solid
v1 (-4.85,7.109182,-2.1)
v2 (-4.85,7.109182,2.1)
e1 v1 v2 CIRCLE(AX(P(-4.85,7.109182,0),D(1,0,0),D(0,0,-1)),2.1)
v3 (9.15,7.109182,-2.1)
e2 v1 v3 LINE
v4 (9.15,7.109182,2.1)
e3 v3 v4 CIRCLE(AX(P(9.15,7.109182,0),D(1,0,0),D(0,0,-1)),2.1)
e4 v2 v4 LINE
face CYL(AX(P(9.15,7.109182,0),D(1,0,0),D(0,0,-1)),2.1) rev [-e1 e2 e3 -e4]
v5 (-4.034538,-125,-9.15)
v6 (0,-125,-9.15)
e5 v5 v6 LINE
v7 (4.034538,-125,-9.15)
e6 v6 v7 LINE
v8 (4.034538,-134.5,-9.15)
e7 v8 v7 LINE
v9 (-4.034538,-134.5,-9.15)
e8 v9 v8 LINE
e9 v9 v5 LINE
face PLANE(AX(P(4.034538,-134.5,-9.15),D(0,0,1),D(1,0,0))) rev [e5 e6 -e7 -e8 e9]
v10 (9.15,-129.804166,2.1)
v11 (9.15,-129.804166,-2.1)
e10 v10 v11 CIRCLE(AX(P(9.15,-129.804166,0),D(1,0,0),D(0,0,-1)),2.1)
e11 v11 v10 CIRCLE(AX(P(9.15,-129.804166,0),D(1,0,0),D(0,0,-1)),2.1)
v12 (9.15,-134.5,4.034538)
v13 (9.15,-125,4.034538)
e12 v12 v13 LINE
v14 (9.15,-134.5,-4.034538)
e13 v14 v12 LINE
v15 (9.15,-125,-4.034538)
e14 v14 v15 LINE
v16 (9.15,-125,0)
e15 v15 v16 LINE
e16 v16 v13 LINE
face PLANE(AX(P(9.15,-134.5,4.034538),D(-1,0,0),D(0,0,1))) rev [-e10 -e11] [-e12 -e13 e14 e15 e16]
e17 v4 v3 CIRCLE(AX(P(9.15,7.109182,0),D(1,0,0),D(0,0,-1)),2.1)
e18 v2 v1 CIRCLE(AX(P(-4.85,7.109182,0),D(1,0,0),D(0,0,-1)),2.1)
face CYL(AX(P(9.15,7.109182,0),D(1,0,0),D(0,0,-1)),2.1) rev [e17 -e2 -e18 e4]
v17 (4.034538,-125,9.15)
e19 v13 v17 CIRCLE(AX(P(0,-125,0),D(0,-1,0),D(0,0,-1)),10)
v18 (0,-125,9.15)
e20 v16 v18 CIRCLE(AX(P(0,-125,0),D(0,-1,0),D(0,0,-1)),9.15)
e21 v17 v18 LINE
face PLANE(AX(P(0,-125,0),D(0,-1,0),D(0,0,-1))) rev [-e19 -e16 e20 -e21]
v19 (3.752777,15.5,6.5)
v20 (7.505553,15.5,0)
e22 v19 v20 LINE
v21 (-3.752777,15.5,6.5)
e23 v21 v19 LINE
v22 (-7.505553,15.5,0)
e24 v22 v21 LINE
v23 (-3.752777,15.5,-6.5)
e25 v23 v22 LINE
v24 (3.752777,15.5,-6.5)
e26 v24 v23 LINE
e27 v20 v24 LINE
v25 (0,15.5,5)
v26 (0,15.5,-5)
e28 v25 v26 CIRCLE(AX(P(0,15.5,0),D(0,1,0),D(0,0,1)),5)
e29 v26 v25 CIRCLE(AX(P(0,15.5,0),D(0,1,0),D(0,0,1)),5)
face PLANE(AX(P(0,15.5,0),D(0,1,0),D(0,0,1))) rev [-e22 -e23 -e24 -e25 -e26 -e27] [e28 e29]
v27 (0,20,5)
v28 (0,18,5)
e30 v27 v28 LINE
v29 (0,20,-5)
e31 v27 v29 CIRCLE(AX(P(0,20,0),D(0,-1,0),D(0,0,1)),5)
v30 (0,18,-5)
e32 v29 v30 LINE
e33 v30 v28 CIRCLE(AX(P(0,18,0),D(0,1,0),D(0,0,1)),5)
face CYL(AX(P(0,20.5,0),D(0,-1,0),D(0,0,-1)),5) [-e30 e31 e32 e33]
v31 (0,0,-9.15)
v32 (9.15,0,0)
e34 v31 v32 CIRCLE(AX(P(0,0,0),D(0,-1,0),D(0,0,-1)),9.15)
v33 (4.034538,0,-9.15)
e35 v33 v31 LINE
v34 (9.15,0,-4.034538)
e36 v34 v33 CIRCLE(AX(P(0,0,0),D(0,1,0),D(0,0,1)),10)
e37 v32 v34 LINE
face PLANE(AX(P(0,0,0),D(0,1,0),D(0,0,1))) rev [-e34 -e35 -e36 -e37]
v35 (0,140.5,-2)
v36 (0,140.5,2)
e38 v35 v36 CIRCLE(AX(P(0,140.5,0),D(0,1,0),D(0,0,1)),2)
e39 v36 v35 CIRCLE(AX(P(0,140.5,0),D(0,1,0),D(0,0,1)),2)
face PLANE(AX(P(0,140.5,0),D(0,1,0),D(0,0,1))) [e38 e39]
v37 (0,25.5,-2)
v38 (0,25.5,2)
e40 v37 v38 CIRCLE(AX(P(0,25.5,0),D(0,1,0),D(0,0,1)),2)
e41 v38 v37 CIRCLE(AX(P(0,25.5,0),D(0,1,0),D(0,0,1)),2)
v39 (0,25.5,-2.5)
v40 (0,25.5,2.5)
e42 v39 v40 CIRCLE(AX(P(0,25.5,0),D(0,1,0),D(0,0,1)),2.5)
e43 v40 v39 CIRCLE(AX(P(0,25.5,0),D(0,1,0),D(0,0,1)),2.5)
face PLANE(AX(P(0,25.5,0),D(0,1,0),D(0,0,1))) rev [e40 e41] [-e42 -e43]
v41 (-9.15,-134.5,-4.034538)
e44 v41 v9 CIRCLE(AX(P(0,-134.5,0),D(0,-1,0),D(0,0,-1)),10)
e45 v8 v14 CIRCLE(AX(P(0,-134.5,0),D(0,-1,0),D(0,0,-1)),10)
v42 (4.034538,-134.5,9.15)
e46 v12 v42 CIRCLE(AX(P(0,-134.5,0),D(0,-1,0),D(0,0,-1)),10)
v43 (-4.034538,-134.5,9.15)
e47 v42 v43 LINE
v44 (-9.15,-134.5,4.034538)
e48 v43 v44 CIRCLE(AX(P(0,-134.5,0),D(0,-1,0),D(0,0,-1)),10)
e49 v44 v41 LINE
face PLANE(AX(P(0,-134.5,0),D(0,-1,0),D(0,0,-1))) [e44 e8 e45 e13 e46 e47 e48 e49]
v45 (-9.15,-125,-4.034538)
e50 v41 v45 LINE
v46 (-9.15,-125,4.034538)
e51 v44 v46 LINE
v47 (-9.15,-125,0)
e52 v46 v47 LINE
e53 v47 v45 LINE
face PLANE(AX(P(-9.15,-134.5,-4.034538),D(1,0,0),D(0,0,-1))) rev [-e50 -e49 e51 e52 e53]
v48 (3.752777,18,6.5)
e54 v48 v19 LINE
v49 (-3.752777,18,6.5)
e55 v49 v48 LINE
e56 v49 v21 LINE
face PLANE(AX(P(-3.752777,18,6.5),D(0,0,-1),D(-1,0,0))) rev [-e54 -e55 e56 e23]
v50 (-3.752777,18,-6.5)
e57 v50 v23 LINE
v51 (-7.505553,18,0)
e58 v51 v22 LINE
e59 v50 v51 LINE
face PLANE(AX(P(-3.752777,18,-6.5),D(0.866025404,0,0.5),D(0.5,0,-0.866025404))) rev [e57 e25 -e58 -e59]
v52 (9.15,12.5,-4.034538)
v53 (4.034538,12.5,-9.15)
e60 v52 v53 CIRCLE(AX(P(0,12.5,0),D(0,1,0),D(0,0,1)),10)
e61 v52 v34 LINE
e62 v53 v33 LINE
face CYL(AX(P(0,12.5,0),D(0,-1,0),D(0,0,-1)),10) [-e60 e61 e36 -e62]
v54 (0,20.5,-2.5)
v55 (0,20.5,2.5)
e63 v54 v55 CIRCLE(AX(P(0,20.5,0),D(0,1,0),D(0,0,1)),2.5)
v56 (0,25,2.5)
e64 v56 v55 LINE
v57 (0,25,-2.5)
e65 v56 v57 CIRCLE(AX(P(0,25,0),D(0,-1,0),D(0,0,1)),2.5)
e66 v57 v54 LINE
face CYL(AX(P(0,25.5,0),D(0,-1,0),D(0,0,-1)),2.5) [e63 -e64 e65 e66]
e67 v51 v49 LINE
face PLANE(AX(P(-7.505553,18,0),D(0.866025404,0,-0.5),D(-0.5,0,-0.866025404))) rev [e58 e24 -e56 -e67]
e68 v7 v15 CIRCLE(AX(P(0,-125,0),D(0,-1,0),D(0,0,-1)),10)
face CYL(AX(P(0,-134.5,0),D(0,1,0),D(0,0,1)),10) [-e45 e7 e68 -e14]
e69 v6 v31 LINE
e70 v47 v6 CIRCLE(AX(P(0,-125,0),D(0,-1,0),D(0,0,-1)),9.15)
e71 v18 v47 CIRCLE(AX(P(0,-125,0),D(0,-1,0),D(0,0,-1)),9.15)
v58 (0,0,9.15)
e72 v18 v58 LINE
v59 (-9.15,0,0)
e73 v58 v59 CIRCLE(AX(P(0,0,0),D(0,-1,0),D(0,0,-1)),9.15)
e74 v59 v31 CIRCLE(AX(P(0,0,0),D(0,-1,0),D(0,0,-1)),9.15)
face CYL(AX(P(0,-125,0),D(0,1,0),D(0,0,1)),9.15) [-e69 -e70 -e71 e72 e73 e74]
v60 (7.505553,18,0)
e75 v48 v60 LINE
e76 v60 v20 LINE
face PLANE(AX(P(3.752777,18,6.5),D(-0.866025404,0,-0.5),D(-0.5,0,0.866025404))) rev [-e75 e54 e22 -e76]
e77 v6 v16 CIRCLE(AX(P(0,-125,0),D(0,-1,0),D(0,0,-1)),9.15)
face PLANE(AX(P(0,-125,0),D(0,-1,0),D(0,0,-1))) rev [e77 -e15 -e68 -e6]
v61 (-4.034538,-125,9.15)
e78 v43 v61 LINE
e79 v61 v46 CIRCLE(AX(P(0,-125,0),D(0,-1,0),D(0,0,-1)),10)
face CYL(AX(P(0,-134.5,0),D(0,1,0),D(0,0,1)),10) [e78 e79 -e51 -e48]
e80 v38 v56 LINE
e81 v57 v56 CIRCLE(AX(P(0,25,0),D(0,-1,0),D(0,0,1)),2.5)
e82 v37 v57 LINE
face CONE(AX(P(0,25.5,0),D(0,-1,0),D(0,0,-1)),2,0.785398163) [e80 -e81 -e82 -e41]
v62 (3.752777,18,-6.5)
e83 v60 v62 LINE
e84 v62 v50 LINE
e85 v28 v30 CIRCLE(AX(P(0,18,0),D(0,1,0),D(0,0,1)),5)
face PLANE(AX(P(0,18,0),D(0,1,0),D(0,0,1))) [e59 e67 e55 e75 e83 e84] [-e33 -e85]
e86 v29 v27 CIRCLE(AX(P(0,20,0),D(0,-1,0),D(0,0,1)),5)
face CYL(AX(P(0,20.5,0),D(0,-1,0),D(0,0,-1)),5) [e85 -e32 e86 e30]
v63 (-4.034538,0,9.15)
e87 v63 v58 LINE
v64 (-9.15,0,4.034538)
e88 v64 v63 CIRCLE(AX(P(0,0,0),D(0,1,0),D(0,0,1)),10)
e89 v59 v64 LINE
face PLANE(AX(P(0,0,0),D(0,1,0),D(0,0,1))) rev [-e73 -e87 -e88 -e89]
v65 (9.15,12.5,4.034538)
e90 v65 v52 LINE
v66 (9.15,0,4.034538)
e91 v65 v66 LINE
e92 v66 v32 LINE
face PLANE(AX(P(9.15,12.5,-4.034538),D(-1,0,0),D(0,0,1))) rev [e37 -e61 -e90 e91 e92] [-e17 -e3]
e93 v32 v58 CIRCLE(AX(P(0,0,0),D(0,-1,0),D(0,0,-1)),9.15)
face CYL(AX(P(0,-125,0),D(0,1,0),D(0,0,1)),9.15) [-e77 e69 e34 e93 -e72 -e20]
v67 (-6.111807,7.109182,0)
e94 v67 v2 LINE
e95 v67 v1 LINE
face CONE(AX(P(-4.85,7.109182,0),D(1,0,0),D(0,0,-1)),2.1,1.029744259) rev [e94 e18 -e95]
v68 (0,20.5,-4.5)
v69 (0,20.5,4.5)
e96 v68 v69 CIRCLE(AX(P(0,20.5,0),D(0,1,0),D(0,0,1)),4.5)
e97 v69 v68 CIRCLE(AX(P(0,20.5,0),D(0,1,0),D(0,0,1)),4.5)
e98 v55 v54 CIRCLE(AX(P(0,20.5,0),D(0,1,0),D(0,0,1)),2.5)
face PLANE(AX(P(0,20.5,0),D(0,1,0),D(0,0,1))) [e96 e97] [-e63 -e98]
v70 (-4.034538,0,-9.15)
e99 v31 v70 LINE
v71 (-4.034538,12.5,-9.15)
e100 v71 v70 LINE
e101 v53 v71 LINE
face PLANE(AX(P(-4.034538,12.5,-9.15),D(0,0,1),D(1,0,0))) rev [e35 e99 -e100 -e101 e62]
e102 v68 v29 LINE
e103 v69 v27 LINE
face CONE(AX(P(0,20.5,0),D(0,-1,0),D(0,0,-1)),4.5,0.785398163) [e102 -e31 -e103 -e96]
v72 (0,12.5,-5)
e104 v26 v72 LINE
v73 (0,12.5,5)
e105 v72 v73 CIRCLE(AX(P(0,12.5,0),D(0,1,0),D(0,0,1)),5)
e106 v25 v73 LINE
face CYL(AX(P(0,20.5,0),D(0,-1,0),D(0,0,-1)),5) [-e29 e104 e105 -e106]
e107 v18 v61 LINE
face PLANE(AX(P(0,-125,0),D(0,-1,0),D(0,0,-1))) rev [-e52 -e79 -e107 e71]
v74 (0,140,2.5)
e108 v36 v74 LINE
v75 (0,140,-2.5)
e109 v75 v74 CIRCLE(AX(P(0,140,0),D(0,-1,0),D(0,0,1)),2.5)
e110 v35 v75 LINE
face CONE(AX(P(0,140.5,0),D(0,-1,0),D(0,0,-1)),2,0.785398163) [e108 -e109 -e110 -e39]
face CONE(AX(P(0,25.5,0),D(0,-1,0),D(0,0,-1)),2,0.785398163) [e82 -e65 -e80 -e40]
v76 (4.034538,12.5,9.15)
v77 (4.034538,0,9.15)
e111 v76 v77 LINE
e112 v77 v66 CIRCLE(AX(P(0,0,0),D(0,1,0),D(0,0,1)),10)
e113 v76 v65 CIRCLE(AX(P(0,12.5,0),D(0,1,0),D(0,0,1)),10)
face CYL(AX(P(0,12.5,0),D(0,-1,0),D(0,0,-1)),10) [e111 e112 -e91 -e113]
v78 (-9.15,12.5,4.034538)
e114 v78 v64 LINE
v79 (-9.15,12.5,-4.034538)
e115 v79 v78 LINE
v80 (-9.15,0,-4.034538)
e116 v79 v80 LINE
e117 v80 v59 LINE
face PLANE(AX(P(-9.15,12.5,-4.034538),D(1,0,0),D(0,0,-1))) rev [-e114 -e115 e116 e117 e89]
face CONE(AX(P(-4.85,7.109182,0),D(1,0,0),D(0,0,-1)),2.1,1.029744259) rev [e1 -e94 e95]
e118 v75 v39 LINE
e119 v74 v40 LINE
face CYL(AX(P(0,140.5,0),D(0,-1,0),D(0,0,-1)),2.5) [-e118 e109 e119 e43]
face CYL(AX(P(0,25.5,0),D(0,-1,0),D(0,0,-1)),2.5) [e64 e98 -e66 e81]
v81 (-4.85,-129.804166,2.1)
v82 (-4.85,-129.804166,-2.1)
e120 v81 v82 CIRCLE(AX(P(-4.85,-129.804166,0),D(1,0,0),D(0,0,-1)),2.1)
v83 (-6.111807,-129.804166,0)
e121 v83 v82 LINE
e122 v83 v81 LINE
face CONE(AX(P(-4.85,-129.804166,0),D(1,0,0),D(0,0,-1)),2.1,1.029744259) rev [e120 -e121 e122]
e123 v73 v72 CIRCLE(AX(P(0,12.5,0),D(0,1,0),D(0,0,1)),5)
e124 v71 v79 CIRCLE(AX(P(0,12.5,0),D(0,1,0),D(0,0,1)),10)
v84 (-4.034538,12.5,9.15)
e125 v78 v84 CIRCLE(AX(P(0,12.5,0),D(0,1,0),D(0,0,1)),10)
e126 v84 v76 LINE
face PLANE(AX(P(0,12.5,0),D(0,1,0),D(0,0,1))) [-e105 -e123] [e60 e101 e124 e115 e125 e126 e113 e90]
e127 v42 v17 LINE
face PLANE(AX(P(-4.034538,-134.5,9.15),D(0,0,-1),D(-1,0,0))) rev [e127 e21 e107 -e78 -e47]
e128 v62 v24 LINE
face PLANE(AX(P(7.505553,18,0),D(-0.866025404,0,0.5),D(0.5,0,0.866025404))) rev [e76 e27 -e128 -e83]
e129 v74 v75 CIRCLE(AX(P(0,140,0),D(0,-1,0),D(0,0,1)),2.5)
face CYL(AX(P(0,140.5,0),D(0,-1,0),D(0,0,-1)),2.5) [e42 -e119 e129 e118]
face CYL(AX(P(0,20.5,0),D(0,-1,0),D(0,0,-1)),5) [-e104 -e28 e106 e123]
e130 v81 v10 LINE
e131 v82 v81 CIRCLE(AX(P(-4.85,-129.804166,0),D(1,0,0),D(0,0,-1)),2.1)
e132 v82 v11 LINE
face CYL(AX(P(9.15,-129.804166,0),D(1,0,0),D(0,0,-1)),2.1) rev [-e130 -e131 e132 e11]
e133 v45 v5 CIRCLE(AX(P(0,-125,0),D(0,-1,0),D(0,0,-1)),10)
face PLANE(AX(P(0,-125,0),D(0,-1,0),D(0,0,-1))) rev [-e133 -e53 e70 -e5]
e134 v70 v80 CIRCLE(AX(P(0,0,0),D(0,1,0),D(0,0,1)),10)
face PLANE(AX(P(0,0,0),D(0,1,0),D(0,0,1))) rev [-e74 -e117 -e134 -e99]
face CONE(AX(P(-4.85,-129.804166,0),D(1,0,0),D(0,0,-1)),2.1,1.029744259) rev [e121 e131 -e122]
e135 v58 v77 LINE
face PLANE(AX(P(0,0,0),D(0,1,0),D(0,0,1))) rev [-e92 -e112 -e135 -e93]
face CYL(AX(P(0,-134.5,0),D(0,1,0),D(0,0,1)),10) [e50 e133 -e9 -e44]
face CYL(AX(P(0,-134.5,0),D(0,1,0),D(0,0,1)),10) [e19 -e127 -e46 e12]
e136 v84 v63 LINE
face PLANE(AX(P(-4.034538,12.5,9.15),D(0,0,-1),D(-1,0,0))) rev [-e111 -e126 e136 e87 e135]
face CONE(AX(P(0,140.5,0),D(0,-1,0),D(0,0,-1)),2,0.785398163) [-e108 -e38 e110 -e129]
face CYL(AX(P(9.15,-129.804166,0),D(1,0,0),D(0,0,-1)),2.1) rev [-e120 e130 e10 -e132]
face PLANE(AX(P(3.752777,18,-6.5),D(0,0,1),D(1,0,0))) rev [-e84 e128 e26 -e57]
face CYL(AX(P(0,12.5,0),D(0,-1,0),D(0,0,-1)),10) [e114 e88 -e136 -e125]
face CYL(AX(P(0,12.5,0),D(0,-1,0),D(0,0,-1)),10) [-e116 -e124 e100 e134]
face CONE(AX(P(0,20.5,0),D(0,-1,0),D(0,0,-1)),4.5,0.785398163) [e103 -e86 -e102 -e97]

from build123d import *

# Parameters (mm, degrees)
BOSS_EXTRUDE1_DEPTH   = 12.5
SKETCH3_R             = 9.15
BOSS_EXTRUDE2_DEPTH   = 125
BOSS_EXTRUDE3_START   = 9.5
BOSS_EXTRUDE3_DEPTH   = 9.5
SKETCH5_R             = 5
BOSS_EXTRUDE4_DEPTH   = 8
SKETCH6_R             = 2.5
BOSS_EXTRUDE5_DEPTH   = 5
CHAMFER1_SIZE         = 0.5
SKETCH8_R             = 2.5
BOSS_EXTRUDE6_DEPTH   = 115
CHAMFER2_SIZE         = 0.5
BOSS_EXTRUDE7_DEPTH   = 2.5
CHAMFER4_SIZE         = 0.5
M5_TAPPED_HOLE1_D     = 4.2
M5_TAPPED_HOLE1_DEPTH = 14
M5_TAPPED_HOLE1_TIP   = 1.2618073


with BuildPart() as part:
    # Sketch1 → Boss-Extrude1 (new body)
    with BuildSketch(Plane(origin=(0, 0, 0), x_dir=(1, 0, 0), z_dir=(0, 1, 0))):
        with BuildLine():
            Line((-4.034538387, 9.15), (4.034538387, 9.15))
            ThreePointArc((4.034538387, 9.15), (7.071067812, 7.071067812), (9.15, 4.034538387))
            Line((9.15, 4.034538387), (9.15, -4.034538387))
            ThreePointArc((9.15, -4.034538387), (7.071067812, -7.071067812), (4.034538387, -9.15))
            Line((4.034538387, -9.15), (-4.034538387, -9.15))
            ThreePointArc((-4.034538387, -9.15), (-7.071067812, -7.071067812), (-9.15, -4.034538387))
            Line((-9.15, -4.034538387), (-9.15, 4.034538387))
            ThreePointArc((-9.15, 4.034538387), (-7.071067812, 7.071067812), (-4.034538387, 9.15))
        make_face()
    extrude(amount=BOSS_EXTRUDE1_DEPTH)

    # Sketch3 → Boss-Extrude2 (add)
    with BuildSketch(Plane.XZ):
        with Locations(Location((0, 0, 0), (0, 0, 270))):
            Circle(SKETCH3_R)
    extrude(amount=BOSS_EXTRUDE2_DEPTH)

    # Sketch4 → Boss-Extrude3 (add)
    with BuildSketch(Plane.XZ.offset(125).offset(BOSS_EXTRUDE3_START)):
        with BuildLine():
            Line((-4.034538387, 9.15), (4.034538387, 9.15))
            ThreePointArc((4.034538387, 9.15), (7.071067812, 7.071067812), (9.15, 4.034538387))
            Line((9.15, 4.034538387), (9.15, -4.034538387))
            ThreePointArc((9.15, -4.034538387), (7.071067812, -7.071067812), (4.034538387, -9.15))
            Line((4.034538387, -9.15), (-4.034538387, -9.15))
            ThreePointArc((-4.034538387, -9.15), (-7.071067812, -7.071067812), (-9.15, -4.034538387))
            Line((-9.15, -4.034538387), (-9.15, 4.034538387))
            ThreePointArc((-9.15, 4.034538387), (-7.071067812, 7.071067812), (-4.034538387, 9.15))
        make_face()
    extrude(amount=-BOSS_EXTRUDE3_DEPTH)

    # Sketch5 → Boss-Extrude4 (add)
    with BuildSketch(Plane(origin=(0, 12.5, 0), x_dir=(1, 0, 0), z_dir=(0, 1, 0))):
        with Locations(Location((0, 0, 0), (0, 0, 270))):
            Circle(SKETCH5_R)
    extrude(amount=BOSS_EXTRUDE4_DEPTH)

    # Sketch6 → Boss-Extrude5 (add)
    with BuildSketch(Plane(origin=(0, 20.5, 0), x_dir=(1, 0, 0), z_dir=(0, 1, 0))):
        with Locations(Location((0, 0, 0), (0, 0, 270))):
            Circle(SKETCH6_R)
    extrude(amount=BOSS_EXTRUDE5_DEPTH)

    # Chamfer1
    chamfer1_edges = [part.edges().sort_by_distance(p)[0] for p in [
        (0, 25.5, -2.5),
    ]]
    chamfer(chamfer1_edges, length=CHAMFER1_SIZE)

    # Sketch8 → Boss-Extrude6 (add)
    with BuildSketch(Plane(origin=(0, 25.5, 0), x_dir=(1, 0, 0), z_dir=(0, 1, 0))):
        with Locations(Location((0, 0, 0), (0, 0, 270))):
            Circle(SKETCH8_R)
    extrude(amount=BOSS_EXTRUDE6_DEPTH)

    # Chamfer2
    chamfer2_edges = [part.edges().sort_by_distance(p)[0] for p in [
        (0, 20.5, -5),
    ]]
    chamfer(chamfer2_edges, length=CHAMFER2_SIZE)

    # Sketch9 → Boss-Extrude7 (add)
    with BuildSketch(Plane(origin=(0, 15.5, 0), x_dir=(1, 0, 0), z_dir=(0, 1, 0))):
        Polygon((7.505553499, 0), (3.75277675, 6.5), (-3.75277675, 6.5), (-7.505553499, 0), (-3.75277675, -6.5), (3.75277675, -6.5), align=None)
    extrude(amount=BOSS_EXTRUDE7_DEPTH)

    # Chamfer4
    chamfer4_edges = [part.edges().sort_by_distance(p)[0] for p in [
        (0, 140.5, -2.5),
    ]]
    chamfer(chamfer4_edges, length=CHAMFER4_SIZE)

    # M5 Tapped Hole1
    with Locations(Plane(origin=(9.15, 0, 0), x_dir=(0, 0, -1), z_dir=(1, 0, 0))):
        with Locations((0, 7.109181896), (0, -129.804166053)):
            Hole(M5_TAPPED_HOLE1_D / 2, depth=M5_TAPPED_HOLE1_DEPTH)
            with Locations((0, 0, -(M5_TAPPED_HOLE1_DEPTH + M5_TAPPED_HOLE1_TIP / 2))):  # 118° drill point
                Cone(0, M5_TAPPED_HOLE1_D / 2, M5_TAPPED_HOLE1_TIP, mode=Mode.SUBTRACT)


solid = part.part
